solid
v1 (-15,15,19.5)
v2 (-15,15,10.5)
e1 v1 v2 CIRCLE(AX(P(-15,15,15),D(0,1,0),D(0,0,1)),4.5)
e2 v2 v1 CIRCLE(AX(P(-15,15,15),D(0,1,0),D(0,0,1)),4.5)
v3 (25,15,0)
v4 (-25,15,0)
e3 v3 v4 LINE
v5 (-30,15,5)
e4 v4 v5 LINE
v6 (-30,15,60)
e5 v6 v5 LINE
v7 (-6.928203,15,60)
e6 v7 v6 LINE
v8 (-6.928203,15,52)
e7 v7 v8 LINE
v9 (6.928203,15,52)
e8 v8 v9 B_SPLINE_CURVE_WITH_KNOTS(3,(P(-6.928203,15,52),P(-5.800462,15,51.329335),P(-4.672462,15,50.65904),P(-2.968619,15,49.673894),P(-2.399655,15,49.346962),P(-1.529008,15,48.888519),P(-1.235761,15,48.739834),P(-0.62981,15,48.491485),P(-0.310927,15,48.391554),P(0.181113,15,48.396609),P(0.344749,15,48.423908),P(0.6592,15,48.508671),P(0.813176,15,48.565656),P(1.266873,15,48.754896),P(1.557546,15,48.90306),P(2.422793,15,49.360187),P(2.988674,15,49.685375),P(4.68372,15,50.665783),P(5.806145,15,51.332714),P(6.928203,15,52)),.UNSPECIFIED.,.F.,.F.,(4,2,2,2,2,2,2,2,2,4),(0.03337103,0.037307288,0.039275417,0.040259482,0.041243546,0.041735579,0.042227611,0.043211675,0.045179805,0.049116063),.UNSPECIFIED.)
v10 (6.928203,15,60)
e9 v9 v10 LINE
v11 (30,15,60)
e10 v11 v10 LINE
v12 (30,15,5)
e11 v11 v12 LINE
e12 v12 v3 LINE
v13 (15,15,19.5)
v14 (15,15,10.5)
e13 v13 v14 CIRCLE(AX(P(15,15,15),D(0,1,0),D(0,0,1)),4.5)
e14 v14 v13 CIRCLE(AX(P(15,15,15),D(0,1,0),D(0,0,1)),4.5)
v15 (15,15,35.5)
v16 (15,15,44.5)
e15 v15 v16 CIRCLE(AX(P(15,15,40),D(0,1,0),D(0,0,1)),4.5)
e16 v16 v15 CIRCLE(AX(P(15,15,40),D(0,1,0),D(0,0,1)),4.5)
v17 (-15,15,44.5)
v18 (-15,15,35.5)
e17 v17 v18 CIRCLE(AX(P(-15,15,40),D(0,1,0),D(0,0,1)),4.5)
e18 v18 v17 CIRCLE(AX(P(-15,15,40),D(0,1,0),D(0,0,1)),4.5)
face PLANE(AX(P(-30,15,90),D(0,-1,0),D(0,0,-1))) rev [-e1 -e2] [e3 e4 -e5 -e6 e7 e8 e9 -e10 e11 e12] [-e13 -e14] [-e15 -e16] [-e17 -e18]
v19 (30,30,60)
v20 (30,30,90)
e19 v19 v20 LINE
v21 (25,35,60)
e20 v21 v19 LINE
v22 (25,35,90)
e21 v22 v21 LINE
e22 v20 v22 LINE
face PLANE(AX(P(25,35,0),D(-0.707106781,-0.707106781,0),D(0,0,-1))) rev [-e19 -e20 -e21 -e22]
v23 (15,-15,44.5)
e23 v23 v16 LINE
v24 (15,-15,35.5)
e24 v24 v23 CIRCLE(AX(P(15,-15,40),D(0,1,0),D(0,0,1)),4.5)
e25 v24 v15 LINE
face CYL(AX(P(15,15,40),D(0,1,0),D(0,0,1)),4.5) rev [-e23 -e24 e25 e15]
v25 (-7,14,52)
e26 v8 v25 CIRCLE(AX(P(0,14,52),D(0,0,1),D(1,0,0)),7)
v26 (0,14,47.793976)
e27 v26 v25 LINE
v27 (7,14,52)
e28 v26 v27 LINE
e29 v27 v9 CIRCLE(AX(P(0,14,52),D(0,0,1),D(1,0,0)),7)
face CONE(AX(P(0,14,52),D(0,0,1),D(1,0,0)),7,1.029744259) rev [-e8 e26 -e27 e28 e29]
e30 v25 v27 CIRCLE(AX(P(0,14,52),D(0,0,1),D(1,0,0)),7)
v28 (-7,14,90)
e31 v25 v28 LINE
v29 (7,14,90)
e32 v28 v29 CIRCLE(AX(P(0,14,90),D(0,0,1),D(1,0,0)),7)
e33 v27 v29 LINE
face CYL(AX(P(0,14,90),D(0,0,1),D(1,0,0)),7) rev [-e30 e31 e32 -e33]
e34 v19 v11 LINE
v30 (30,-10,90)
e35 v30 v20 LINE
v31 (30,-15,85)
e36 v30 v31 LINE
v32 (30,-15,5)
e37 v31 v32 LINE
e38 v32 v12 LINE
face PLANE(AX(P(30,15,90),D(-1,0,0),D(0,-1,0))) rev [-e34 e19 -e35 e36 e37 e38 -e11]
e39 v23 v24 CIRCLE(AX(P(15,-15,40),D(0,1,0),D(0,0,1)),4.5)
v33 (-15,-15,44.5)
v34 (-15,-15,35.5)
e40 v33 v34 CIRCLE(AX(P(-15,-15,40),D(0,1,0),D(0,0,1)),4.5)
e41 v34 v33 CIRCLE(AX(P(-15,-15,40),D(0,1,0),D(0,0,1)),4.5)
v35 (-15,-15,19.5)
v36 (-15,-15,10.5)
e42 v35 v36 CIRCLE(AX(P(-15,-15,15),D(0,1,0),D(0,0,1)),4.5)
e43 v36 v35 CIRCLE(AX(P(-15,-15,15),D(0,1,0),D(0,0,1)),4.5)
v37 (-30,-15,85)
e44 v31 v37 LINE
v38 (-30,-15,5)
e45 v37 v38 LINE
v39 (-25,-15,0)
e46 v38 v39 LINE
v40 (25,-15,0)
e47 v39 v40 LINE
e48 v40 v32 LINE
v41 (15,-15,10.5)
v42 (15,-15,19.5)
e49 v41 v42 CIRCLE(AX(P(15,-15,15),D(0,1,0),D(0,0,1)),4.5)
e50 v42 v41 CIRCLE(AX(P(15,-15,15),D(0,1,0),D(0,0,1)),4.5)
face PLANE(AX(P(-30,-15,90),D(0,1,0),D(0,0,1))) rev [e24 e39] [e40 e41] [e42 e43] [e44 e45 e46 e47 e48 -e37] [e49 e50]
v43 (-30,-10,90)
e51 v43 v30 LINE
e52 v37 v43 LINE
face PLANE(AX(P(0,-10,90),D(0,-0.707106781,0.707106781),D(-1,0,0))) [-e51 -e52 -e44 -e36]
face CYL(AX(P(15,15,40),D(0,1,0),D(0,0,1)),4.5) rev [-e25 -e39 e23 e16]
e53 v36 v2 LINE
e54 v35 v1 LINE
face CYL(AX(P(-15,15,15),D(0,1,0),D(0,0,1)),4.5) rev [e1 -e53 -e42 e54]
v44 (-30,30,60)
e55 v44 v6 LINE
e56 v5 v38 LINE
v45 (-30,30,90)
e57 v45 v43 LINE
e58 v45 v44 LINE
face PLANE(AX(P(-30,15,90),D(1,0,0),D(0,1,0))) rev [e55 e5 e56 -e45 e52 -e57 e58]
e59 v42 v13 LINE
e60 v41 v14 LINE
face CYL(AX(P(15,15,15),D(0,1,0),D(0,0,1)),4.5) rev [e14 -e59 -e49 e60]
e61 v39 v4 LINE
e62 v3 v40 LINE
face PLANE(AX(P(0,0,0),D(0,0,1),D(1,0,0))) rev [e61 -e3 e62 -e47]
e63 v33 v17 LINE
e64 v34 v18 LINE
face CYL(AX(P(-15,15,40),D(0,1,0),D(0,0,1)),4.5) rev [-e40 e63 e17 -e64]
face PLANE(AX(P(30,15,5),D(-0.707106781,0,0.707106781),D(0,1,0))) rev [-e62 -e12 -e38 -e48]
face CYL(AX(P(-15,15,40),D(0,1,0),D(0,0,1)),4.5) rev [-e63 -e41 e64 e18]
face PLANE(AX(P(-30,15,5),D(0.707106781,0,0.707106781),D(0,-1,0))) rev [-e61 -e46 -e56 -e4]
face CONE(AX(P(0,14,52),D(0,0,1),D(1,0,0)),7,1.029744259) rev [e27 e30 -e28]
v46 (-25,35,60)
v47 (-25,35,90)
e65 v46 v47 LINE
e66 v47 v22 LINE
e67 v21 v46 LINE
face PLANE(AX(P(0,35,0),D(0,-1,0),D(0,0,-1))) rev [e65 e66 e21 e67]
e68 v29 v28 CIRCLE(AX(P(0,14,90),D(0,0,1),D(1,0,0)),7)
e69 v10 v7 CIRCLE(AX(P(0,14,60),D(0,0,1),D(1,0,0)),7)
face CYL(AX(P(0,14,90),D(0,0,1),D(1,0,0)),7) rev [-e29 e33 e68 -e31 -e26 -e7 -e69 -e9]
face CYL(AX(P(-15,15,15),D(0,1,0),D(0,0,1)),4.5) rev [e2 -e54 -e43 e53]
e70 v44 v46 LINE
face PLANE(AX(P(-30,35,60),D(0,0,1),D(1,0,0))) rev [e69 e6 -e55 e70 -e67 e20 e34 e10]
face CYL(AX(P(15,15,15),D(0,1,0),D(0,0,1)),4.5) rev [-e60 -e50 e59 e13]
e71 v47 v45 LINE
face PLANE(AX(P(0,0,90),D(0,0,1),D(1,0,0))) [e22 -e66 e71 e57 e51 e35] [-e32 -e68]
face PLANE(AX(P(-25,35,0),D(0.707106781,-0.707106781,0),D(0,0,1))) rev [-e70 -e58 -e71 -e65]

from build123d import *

# Parameters (mm, degrees)
SKETCH_1_W              = 60
SKETCH_1_H              = 30
EXTRUDE_1_DEPTH         = 90
SKETCH_2_W              = 60
SKETCH_2_H              = 30
EXTRUDE_2_DEPTH         = 20
HOLE_WIZARD_9_0_9_1_D   = 9
HOLE_WIZARD_M16_1_D     = 14
HOLE_WIZARD_M16_1_DEPTH = 38
HOLE_WIZARD_M16_1_TIP   = 4.206024333
CHAMFER_1_SIZE          = 5
CHAMFER_2_SIZE          = 5


with BuildPart() as part:
    # 草图1 → 凸台-拉伸1 (new body)
    with BuildSketch(Plane.XY):
        Rectangle(SKETCH_1_W, SKETCH_1_H)
    extrude(amount=EXTRUDE_1_DEPTH)

    # 草图2 → 凸台-拉伸2 (add)
    with BuildSketch(Plane(origin=(0, 15, 0), x_dir=(1, 0, 0), z_dir=(0, 1, 0))):
        with Locations((0, -75)):
            Rectangle(SKETCH_2_W, SKETCH_2_H)
    extrude(amount=EXTRUDE_2_DEPTH)

    # Ø9.0 (9) 直径孔1 (through all)
    with Locations(Plane(origin=(0, 15, 0), x_dir=(1, 0, 0), z_dir=(0, 1, 0))):
        with Locations((-15, -15), (15, -15), (-15, -40), (15, -40)):
            Hole(HOLE_WIZARD_9_0_9_1_D / 2)

    # M16 螺纹孔1
    with Locations(Plane.XY.offset(90)):
        with Locations((0, 14)):
            Hole(HOLE_WIZARD_M16_1_D / 2, depth=HOLE_WIZARD_M16_1_DEPTH)
            with Locations((0, 0, -(HOLE_WIZARD_M16_1_DEPTH + HOLE_WIZARD_M16_1_TIP / 2))):  # 118° drill point
                Cone(0, HOLE_WIZARD_M16_1_D / 2, HOLE_WIZARD_M16_1_TIP, mode=Mode.SUBTRACT)

    # 倒角1
    chamfer_1_edges = [part.edges().sort_by_distance(p)[0] for p in [
        (-30, 35, 75),
        (30, 35, 75),
        (-30, 0, 0),
        (30, 0, 0),
    ]]
    chamfer(chamfer_1_edges, length=CHAMFER_1_SIZE)

    # 倒角2
    chamfer_2_edges = [part.edges().sort_by_distance(p)[0] for p in [
        (0, -15, 90),
    ]]
    chamfer(chamfer_2_edges, length=CHAMFER_2_SIZE)


solid = part.part
